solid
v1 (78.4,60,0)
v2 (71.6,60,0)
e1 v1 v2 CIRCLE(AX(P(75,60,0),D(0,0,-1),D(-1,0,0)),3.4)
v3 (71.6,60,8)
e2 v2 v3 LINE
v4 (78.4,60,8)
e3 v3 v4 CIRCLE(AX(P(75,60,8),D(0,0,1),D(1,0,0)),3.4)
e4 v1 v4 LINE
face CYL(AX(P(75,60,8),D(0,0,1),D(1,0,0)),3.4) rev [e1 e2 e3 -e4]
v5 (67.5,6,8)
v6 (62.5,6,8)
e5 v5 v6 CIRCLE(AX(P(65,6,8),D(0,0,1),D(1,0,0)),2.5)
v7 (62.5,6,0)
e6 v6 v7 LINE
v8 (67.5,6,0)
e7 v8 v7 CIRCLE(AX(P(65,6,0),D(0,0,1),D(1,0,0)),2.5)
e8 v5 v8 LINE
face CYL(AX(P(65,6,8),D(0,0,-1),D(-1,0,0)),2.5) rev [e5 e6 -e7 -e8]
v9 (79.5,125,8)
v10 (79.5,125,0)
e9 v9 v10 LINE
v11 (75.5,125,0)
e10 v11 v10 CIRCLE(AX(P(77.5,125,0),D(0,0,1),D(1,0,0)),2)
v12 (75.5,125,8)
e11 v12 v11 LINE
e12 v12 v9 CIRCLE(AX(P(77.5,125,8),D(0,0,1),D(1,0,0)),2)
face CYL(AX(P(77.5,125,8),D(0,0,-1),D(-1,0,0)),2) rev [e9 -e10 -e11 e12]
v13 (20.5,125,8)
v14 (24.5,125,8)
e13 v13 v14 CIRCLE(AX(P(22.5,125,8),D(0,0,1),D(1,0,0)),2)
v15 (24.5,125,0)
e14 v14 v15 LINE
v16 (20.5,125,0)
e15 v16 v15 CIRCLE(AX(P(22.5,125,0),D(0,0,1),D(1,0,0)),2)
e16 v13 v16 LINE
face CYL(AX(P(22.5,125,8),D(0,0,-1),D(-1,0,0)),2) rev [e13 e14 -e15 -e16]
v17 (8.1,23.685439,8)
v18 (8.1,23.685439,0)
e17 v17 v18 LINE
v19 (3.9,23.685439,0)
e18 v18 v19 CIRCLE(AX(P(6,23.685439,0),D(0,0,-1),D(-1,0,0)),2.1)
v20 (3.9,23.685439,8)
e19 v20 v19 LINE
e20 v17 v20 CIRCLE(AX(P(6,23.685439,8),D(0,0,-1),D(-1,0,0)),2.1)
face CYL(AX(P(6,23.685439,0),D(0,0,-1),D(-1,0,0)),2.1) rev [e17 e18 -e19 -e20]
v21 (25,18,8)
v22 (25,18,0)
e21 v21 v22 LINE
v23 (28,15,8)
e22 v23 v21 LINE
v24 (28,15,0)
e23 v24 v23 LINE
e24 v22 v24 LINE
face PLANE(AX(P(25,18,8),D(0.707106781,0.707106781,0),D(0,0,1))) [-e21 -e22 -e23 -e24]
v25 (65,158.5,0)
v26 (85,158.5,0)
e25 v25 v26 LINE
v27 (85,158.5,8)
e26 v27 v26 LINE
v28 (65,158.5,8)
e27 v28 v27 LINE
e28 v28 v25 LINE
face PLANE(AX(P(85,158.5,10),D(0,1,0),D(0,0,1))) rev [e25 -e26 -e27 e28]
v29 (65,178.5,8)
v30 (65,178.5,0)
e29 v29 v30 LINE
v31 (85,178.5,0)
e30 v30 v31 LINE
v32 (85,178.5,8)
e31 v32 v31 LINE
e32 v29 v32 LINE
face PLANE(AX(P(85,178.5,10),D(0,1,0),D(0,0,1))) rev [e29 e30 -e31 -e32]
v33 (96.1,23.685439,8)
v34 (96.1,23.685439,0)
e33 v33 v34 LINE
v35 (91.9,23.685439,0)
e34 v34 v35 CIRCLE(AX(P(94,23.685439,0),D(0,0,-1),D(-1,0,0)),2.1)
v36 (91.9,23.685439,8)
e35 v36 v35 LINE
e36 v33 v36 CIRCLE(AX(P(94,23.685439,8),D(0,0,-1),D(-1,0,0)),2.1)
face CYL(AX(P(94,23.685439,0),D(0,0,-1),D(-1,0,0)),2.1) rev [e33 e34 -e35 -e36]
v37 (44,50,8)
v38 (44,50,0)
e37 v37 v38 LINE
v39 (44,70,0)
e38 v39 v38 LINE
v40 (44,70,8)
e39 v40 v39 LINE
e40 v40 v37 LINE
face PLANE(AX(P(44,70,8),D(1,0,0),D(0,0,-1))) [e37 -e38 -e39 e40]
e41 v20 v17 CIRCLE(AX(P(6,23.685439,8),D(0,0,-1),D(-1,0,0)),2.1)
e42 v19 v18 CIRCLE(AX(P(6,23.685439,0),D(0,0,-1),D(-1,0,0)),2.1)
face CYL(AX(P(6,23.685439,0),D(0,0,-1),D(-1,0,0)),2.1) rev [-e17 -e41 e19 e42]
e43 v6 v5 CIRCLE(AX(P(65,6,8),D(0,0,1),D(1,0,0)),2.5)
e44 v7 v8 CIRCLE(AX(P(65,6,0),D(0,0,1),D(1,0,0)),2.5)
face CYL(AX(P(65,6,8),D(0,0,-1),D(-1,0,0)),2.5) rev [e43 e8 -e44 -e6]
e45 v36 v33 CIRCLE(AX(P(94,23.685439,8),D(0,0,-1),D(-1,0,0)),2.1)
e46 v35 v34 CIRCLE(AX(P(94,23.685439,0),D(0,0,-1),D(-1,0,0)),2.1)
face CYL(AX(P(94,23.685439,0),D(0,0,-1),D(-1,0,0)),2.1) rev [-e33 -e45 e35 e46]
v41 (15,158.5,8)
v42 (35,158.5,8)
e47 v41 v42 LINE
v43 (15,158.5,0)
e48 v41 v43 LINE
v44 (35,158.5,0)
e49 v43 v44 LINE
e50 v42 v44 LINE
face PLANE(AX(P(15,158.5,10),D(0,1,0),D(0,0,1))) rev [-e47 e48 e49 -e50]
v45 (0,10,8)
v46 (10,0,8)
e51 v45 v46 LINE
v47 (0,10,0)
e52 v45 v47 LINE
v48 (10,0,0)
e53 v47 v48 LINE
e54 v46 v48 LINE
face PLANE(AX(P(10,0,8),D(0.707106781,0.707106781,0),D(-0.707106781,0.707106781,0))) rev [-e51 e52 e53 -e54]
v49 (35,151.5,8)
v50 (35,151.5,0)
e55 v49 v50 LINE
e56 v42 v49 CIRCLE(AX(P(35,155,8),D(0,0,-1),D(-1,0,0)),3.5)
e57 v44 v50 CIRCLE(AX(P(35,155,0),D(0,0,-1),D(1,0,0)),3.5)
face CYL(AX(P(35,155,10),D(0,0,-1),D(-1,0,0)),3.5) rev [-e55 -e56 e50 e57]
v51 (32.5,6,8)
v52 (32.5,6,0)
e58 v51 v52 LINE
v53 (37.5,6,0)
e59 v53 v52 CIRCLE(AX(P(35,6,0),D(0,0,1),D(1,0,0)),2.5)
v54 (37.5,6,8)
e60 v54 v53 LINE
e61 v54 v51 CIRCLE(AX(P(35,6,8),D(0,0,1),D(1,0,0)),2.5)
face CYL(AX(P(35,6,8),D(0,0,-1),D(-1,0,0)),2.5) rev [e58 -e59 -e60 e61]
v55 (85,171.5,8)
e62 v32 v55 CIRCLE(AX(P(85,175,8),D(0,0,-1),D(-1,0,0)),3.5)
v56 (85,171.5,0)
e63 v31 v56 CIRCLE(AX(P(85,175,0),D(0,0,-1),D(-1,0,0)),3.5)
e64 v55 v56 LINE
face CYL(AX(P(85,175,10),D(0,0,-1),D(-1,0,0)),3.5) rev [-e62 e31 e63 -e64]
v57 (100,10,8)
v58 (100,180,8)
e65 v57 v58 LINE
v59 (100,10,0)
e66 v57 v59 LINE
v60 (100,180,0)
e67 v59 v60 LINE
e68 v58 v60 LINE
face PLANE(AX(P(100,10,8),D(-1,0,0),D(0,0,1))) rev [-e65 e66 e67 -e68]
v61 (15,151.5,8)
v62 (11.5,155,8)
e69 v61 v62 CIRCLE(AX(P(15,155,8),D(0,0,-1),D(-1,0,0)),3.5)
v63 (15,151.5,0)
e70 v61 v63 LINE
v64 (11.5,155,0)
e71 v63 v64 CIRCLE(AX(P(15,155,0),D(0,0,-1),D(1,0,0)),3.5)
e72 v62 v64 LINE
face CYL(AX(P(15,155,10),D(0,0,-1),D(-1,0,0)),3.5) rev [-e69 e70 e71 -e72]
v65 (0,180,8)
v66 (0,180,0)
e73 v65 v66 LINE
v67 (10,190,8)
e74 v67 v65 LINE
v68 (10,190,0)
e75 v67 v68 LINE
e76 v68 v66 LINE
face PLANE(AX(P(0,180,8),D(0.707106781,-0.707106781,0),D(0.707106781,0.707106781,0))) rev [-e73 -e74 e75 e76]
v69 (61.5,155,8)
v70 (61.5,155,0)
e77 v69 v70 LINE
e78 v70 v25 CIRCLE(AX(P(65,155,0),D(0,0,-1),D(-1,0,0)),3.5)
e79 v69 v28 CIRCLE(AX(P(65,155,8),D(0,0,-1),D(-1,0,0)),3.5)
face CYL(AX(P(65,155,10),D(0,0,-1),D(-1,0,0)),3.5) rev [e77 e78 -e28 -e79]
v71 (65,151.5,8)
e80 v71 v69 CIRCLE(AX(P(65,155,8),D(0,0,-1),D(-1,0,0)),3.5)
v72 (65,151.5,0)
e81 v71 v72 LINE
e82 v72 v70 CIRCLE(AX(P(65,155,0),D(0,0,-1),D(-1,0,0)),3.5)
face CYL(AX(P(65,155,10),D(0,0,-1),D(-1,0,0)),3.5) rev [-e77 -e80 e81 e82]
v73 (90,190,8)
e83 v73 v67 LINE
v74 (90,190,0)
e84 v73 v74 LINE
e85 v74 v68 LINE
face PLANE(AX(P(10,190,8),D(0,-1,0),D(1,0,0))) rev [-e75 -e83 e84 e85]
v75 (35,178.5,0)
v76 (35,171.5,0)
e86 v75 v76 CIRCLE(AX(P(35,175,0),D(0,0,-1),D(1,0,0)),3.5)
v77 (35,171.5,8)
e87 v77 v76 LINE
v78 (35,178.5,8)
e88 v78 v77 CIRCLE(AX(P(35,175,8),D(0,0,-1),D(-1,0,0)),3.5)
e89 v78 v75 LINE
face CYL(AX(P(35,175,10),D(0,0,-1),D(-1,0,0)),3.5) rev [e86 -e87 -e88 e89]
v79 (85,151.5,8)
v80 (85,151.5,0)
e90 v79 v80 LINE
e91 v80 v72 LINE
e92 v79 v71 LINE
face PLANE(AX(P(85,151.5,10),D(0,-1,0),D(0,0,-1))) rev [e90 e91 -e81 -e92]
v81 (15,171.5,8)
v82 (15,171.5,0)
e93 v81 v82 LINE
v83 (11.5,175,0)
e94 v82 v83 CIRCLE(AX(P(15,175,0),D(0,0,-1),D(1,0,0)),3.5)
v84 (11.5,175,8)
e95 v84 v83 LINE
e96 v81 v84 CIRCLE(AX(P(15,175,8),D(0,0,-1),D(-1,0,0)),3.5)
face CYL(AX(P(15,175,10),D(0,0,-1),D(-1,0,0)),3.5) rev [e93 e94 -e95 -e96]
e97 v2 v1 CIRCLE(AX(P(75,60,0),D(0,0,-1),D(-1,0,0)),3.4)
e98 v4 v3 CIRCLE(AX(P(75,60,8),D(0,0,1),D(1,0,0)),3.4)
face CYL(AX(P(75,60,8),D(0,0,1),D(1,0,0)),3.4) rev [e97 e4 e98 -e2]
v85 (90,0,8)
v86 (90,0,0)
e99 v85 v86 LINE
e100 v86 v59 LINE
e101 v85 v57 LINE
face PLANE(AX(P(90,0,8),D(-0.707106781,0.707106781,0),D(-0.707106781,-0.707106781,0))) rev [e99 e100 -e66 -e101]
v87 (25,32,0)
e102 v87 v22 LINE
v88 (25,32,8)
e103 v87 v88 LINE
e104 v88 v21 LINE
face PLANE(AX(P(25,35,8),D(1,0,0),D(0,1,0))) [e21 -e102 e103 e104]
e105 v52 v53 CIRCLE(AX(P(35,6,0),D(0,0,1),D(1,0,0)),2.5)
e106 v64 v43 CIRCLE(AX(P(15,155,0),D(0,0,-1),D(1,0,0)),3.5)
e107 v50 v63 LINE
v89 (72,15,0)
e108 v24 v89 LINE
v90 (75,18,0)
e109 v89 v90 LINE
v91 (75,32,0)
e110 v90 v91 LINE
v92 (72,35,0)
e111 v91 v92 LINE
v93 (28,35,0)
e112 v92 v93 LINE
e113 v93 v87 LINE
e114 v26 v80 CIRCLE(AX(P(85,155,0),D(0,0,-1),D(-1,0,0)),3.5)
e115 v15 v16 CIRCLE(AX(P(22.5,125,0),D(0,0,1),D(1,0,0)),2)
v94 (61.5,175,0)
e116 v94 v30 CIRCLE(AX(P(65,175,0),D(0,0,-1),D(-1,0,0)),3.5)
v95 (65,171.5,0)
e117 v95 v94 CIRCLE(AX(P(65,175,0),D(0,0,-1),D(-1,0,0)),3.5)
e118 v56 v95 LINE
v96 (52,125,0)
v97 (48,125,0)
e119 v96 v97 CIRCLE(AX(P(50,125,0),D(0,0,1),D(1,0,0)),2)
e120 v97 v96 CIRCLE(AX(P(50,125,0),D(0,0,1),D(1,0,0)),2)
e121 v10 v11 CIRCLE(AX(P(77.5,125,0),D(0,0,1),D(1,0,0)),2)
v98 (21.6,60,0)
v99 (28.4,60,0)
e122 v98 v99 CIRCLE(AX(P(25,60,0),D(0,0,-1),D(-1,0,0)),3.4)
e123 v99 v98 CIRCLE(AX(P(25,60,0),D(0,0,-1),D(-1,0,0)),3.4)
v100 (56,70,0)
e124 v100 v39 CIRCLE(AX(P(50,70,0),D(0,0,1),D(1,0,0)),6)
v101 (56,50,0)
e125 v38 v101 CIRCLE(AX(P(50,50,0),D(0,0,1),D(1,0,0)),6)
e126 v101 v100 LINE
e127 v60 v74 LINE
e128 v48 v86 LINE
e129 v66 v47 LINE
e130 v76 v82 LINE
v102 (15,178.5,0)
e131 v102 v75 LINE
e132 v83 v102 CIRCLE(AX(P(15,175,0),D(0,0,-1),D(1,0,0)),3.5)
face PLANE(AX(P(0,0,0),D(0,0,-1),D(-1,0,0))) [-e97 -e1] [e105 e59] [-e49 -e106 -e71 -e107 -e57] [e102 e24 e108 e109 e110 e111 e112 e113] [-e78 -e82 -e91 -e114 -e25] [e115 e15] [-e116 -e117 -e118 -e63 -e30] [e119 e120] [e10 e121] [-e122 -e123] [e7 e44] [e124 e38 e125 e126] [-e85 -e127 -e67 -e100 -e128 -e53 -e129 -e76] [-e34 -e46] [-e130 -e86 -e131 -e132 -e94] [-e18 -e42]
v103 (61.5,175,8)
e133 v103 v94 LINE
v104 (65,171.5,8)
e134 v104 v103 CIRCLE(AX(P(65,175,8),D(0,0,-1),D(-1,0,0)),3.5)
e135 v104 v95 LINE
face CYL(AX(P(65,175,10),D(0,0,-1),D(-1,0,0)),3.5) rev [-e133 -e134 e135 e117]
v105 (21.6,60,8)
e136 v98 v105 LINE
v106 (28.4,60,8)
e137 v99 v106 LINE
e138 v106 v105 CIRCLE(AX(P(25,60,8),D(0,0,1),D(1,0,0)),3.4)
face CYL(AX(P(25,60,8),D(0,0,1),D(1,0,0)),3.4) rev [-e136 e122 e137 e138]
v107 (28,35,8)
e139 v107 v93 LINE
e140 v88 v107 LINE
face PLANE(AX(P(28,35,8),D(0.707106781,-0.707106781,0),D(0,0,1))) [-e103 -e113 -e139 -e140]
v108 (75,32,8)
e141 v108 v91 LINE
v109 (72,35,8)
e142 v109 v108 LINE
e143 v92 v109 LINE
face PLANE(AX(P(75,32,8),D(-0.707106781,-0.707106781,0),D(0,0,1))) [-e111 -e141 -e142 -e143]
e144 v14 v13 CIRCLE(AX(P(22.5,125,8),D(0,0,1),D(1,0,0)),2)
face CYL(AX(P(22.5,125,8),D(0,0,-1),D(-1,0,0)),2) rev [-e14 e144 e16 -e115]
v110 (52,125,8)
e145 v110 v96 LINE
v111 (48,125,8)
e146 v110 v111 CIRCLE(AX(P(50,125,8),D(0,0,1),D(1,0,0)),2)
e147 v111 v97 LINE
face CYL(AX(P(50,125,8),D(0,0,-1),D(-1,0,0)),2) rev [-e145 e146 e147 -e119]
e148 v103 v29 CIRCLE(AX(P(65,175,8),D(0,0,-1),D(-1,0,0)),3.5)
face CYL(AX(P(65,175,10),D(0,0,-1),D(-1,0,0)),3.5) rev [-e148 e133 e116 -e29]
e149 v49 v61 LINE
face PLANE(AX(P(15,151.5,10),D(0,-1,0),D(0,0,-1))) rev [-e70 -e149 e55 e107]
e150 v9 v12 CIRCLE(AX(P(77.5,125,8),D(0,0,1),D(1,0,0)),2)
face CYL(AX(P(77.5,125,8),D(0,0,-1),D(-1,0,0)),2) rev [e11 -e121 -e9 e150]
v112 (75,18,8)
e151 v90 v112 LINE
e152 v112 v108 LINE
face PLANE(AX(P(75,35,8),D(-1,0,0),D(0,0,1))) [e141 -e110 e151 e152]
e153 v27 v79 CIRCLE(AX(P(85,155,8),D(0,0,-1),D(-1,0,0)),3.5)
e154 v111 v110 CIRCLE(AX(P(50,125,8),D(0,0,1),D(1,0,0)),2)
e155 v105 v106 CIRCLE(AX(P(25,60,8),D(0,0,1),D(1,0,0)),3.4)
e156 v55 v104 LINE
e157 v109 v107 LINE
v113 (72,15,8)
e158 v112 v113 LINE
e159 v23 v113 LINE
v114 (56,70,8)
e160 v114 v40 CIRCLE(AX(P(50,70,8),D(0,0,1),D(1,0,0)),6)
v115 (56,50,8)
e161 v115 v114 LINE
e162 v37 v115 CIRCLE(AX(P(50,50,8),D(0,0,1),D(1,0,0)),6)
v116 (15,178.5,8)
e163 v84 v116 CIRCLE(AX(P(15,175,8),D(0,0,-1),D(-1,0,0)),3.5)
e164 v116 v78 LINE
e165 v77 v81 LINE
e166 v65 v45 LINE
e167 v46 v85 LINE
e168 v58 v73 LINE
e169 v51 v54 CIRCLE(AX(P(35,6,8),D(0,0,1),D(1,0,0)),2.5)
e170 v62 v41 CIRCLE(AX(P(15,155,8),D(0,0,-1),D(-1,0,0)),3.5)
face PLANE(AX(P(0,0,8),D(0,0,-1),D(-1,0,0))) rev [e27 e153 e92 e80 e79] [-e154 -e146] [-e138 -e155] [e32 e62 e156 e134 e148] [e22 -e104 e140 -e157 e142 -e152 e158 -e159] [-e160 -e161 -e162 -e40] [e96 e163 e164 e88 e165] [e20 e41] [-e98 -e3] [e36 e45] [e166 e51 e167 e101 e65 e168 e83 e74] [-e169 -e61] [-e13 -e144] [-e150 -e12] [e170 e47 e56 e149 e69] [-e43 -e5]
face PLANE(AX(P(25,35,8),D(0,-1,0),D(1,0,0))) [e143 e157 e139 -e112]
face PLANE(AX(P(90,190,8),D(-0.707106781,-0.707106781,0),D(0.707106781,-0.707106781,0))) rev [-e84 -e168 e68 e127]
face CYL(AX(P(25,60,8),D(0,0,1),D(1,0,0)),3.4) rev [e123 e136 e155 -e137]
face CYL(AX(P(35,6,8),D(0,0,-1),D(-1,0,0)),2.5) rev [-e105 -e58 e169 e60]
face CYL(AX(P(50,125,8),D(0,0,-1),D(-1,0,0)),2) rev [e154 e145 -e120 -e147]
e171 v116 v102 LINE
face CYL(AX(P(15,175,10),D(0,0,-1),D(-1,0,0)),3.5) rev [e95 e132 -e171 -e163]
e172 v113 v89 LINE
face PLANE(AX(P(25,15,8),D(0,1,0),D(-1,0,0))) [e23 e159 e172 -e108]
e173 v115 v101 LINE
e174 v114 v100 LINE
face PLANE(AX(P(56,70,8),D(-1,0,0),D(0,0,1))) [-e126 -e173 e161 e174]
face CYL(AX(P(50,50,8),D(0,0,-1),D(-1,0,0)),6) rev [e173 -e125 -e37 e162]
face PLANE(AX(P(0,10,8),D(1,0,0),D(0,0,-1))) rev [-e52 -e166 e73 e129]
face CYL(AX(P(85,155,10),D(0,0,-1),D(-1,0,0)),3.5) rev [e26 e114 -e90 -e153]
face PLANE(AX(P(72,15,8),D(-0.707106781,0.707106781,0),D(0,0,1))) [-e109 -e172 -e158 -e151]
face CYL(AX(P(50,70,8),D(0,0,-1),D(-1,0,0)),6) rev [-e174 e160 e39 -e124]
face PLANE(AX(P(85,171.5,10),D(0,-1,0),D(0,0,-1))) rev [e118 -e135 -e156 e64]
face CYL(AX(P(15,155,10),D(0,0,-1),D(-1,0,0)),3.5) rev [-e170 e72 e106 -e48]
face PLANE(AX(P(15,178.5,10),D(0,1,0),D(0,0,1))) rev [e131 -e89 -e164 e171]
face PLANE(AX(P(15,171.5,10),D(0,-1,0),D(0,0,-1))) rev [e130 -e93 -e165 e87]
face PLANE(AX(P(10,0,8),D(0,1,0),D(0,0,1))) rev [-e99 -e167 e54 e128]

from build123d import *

# Parameters (mm, degrees)
SKETCH1_R                   = 2.5
SKETCH1_R_2                 = 2
SKETCH1_W                   = 50
SKETCH1_H                   = 20
BOSS_EXTRUDE1_DEPTH         = 8
CHAMFER1_SIZE               = 3
TAP_DRILL_FOR_M8_TAP1_D     = 6.8
TAP_DRILL_FOR_M8_TAP1_DEPTH = 15
TAP_DRILL_FOR_M8_TAP1_TIP   = 2.042926105
TAP_DRILL_FOR_M5_TAP1_D     = 4.2
TAP_DRILL_FOR_M5_TAP1_DEPTH = 15
TAP_DRILL_FOR_M5_TAP1_TIP   = 1.2618073
CUT_EXTRUDE1_DEPTH          = 10
LPATTERN1_COUNT             = 2
LPATTERN1_PITCH             = 20


with BuildPart() as part:
    # Sketch1 → Boss-Extrude1 (new body)
    with BuildSketch(Plane.XY):
        Polygon((0, 180), (10, 190), (90, 190), (100, 180), (100, 10), (90, 0), (10, 0), (0, 10), align=None)
        with Locations((35, 6)):
            Circle(SKETCH1_R, mode=Mode.SUBTRACT)
        with Locations((65, 6)):
            Circle(SKETCH1_R, mode=Mode.SUBTRACT)
        with Locations((22.5, 125)):
            Circle(SKETCH1_R_2, mode=Mode.SUBTRACT)
        with Locations((50, 125)):
            Circle(SKETCH1_R_2, mode=Mode.SUBTRACT)
        with Locations((77.5, 125)):
            Circle(SKETCH1_R_2, mode=Mode.SUBTRACT)
        with Locations((50, 25)):
            Rectangle(SKETCH1_W, SKETCH1_H, mode=Mode.SUBTRACT)
        with BuildLine():
            Line((56, 70), (56, 50))
            ThreePointArc((56, 50), (50, 44), (44, 50))
            Line((44, 50), (44, 70))
            ThreePointArc((44, 70), (50, 76), (56, 70))
        make_face(mode=Mode.SUBTRACT)
    extrude(amount=BOSS_EXTRUDE1_DEPTH)

    # Chamfer1
    chamfer1_edges = [part.edges().sort_by_distance(p)[0] for p in [
        (25, 35, 4),
        (25, 15, 4),
        (75, 15, 4),
        (75, 35, 4),
    ]]
    chamfer(chamfer1_edges, length=CHAMFER1_SIZE)

    # Tap Drill for M8 Tap1
    with Locations(Plane(origin=(25, 60, 8), x_dir=(1, 0, 0), z_dir=(0, 0, 1))):
        with Locations((0, 0), (50, 0)):
            Hole(TAP_DRILL_FOR_M8_TAP1_D / 2, depth=TAP_DRILL_FOR_M8_TAP1_DEPTH)
            with Locations((0, 0, -(TAP_DRILL_FOR_M8_TAP1_DEPTH + TAP_DRILL_FOR_M8_TAP1_TIP / 2))):  # 118° drill point
                Cone(0, TAP_DRILL_FOR_M8_TAP1_D / 2, TAP_DRILL_FOR_M8_TAP1_TIP, mode=Mode.SUBTRACT)

    # Tap Drill for M5 Tap1
    with Locations(Plane(origin=(94, 23.685438565, 0), x_dir=(-1, 0, 0), z_dir=(0, 0, -1))):
        with Locations((0, 0), (88, 0)):
            Hole(TAP_DRILL_FOR_M5_TAP1_D / 2, depth=TAP_DRILL_FOR_M5_TAP1_DEPTH)
            with Locations((0, 0, -(TAP_DRILL_FOR_M5_TAP1_DEPTH + TAP_DRILL_FOR_M5_TAP1_TIP / 2))):  # 118° drill point
                Cone(0, TAP_DRILL_FOR_M5_TAP1_D / 2, TAP_DRILL_FOR_M5_TAP1_TIP, mode=Mode.SUBTRACT)

    # Sketch5 → Cut-Extrude1 (cut)
    with BuildSketch(Plane(origin=(0, 0, 0), x_dir=(-1, 0, 0), z_dir=(0, 0, -1))):
        with BuildLine():
            Line((-85, 178.5), (-65, 178.5))
            ThreePointArc((-65, 178.5), (-61.5, 175), (-65, 171.5))
            Line((-65, 171.5), (-85, 171.5))
            ThreePointArc((-85, 171.5), (-88.5, 175), (-85, 178.5))
        make_face()
        with BuildLine():
            Line((-15, 178.5), (-35, 178.5))
            ThreePointArc((-35, 178.5), (-38.5, 175), (-35, 171.5))
            Line((-35, 171.5), (-15, 171.5))
            ThreePointArc((-15, 171.5), (-11.5, 175), (-15, 178.5))
        make_face()
    cut_extrude1 = extrude(amount=-CUT_EXTRUDE1_DEPTH, mode=Mode.SUBTRACT)

    # LPattern1: Cut-Extrude1 ×2
    with Locations(*[(0, -i * LPATTERN1_PITCH, 0) for i in range(1, LPATTERN1_COUNT)]):
        add(cut_extrude1, mode=Mode.SUBTRACT)


solid = part.part
